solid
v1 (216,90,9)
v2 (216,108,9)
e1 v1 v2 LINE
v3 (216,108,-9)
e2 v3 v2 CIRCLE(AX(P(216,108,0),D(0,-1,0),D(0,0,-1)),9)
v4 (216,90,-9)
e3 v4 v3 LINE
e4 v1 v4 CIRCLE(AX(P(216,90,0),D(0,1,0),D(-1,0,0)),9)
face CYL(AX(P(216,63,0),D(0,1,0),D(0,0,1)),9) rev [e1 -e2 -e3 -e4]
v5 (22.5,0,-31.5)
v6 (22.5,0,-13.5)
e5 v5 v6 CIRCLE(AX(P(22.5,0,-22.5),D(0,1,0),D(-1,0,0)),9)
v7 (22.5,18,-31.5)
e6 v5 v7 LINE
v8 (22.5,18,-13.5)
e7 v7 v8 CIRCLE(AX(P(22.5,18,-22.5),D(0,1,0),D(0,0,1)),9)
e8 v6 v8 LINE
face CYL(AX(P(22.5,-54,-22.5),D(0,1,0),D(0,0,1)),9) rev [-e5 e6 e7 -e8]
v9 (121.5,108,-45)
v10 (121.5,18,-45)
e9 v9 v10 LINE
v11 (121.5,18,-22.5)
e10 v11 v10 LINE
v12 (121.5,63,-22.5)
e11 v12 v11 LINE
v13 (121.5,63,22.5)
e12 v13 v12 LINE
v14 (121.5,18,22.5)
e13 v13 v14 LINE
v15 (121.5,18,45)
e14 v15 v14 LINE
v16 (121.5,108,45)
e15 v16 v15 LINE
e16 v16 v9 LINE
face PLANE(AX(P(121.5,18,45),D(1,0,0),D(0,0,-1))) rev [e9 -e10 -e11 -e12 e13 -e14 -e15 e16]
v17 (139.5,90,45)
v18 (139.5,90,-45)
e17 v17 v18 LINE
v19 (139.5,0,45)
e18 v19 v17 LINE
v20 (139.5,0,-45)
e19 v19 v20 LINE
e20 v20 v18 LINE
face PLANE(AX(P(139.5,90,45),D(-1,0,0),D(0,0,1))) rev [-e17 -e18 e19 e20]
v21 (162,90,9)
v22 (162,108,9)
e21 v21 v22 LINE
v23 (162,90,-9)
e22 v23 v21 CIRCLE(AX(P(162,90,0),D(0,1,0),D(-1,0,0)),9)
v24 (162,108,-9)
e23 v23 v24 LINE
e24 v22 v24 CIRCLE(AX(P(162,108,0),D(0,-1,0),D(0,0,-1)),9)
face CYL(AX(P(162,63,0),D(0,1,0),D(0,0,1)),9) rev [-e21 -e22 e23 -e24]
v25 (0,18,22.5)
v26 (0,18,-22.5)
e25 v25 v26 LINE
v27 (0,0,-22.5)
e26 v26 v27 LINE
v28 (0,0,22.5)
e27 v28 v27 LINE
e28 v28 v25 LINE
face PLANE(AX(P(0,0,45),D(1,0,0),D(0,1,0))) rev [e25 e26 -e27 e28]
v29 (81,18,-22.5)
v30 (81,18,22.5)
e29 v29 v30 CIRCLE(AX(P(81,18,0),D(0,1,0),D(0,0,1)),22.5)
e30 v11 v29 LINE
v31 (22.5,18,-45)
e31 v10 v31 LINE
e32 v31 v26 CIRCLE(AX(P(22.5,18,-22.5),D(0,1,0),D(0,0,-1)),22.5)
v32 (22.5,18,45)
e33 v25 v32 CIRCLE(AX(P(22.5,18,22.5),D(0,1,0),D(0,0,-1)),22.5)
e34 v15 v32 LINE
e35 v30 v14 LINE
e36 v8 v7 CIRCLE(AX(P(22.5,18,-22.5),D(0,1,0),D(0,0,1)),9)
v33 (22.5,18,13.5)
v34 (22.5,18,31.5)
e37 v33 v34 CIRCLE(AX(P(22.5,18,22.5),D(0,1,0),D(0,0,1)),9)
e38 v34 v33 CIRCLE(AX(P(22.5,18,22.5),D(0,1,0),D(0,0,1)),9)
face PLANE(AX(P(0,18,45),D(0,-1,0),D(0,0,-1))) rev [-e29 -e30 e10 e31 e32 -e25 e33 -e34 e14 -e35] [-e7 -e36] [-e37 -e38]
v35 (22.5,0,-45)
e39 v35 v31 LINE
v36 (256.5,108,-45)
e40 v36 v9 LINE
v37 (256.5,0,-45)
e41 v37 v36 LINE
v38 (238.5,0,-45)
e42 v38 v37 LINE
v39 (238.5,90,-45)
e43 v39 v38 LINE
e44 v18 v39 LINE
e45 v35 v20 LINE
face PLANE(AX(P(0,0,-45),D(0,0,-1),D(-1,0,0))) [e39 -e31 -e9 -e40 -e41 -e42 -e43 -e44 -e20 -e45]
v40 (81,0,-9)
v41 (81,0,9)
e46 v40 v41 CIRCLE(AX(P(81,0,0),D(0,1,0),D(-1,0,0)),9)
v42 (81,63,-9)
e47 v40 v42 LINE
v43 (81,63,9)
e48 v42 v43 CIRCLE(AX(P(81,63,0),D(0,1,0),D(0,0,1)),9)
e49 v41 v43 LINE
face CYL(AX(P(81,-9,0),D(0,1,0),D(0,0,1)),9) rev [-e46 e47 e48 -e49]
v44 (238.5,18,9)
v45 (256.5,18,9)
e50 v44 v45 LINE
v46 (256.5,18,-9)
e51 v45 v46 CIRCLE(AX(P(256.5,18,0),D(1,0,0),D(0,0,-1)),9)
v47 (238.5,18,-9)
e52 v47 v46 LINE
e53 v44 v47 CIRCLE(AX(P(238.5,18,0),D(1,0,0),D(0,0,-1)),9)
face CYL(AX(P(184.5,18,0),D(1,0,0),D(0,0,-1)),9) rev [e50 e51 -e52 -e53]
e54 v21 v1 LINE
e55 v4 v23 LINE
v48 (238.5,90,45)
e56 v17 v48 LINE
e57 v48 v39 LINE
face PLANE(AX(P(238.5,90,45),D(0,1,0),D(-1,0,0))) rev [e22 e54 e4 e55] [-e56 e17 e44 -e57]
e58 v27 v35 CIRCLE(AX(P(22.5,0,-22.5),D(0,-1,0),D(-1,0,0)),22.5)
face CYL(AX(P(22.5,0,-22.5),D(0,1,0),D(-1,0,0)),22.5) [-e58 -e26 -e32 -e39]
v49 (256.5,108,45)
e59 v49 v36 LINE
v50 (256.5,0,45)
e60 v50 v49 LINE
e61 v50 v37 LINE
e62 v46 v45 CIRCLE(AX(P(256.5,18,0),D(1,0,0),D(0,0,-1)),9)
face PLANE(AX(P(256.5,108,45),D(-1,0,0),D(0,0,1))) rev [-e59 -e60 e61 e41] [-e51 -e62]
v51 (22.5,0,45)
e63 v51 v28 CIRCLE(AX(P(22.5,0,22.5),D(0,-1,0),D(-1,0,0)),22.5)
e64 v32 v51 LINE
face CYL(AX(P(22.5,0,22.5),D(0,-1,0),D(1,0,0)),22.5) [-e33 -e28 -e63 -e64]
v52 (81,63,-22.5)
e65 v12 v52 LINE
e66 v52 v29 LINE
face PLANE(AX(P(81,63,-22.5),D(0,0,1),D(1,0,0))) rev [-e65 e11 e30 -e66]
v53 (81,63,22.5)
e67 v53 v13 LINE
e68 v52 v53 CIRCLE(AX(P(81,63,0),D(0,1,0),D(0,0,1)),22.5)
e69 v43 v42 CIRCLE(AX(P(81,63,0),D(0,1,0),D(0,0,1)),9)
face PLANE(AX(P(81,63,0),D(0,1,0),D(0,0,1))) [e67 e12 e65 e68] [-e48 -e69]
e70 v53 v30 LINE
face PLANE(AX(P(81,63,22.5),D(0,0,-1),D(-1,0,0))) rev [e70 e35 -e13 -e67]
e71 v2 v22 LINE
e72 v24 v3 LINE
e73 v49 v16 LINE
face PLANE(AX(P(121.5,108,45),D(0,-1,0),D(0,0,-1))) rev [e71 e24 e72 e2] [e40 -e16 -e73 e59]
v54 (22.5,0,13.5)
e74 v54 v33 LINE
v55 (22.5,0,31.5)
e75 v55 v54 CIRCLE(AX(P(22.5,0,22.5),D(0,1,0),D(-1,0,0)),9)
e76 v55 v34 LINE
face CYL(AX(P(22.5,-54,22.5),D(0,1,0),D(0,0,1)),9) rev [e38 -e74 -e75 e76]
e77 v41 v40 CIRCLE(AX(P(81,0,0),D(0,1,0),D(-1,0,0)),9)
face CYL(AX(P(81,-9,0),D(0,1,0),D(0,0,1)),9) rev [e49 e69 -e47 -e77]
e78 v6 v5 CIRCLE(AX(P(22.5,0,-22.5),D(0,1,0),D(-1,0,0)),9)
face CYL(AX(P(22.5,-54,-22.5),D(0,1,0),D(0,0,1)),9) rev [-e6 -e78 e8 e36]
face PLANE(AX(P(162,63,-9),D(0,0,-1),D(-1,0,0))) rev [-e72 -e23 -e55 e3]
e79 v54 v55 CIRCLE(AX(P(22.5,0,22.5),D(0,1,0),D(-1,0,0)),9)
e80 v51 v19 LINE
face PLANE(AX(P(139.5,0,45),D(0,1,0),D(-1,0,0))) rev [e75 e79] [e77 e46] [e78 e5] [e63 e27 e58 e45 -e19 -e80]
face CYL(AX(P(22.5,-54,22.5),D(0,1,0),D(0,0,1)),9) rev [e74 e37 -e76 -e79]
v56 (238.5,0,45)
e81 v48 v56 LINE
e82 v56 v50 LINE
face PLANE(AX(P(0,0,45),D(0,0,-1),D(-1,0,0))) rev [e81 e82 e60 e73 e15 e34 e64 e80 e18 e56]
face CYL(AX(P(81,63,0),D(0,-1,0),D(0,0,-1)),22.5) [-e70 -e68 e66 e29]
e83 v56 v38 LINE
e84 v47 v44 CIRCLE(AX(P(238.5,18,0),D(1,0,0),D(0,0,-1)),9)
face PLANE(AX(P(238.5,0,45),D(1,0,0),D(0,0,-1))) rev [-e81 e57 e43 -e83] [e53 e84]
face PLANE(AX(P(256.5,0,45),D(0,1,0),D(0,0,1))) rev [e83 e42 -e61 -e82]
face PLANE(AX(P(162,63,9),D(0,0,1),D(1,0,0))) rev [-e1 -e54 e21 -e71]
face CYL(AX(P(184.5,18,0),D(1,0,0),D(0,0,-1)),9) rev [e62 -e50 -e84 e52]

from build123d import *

# Parameters (mm, degrees)
BRACKET_BODY_DEPTH            = 45
TOP_SLOT_18X72_DEPTH          = 45
PIVOT_BOSS_DEPTH              = 45
PIVOT_BORE_SKETCH_R           = 9
PIVOT_BORE_18_DEPTH           = 72
FLANGE_CORNER_FILLETS_R22_5_R = 22.5
FLANGE_HOLES_SKETCH_R         = 9
FLANGE_HOLES_2X_18_DEPTH      = 72
SIDE_HOLE_SKETCH_R            = 9
SIDE_HOLE_18_DEPTH            = 72


with BuildPart() as part:
    # Bracket Profile Sketch → Bracket Body (new, symmetric)
    with BuildSketch(Plane.XY):
        Polygon((0, 0), (0, 18), (121.5, 18), (121.5, 108), (256.5, 108), (256.5, 0), (238.5, 0), (238.5, 90), (139.5, 90), (139.5, 0), align=None)
    extrude(amount=BRACKET_BODY_DEPTH, both=True)

    # Top Slot Sketch → Top Slot 18x72 (cut, symmetric)
    with BuildSketch(Plane(origin=(0, 108, 0), x_dir=(1, 0, 0), z_dir=(0, 1, 0))):
        with BuildLine():
            Line((162, 9), (216, 9))
            ThreePointArc((216, 9), (225, 0), (216, -9))
            Line((216, -9), (162, -9))
            ThreePointArc((162, -9), (153, 0), (162, 9))
        make_face()
    extrude(amount=TOP_SLOT_18X72_DEPTH, both=True, mode=Mode.SUBTRACT)

    # Pivot Boss Sketch → Pivot Boss (add)
    with BuildSketch(Plane(origin=(0, 18, 0), x_dir=(1, 0, 0), z_dir=(0, 1, 0))):
        with BuildLine():
            Line((81, 22.5), (121.5, 22.5))
            Line((121.5, 22.5), (121.5, -22.5))
            Line((121.5, -22.5), (81, -22.5))
            ThreePointArc((81, -22.5), (58.5, 0), (81, 22.5))
        make_face()
    extrude(amount=PIVOT_BOSS_DEPTH)

    # Pivot Bore Sketch → Pivot Bore Ø18 (cut)
    with BuildSketch(Plane(origin=(0, 63, 0), x_dir=(1, 0, 0), z_dir=(0, 1, 0))):
        with Locations(Location((81, 0, 0), (0, 0, 270))):
            Circle(PIVOT_BORE_SKETCH_R)
    extrude(amount=-PIVOT_BORE_18_DEPTH, mode=Mode.SUBTRACT)

    # Flange Corner Fillets R22.5
    flange_corner_fillets_r22_5_edges = [part.edges().sort_by_distance(p)[0] for p in [
        (0, 9, -45),
        (0, 9, 45),
    ]]
    fillet(flange_corner_fillets_r22_5_edges, radius=FLANGE_CORNER_FILLETS_R22_5_R)

    # Flange Holes Sketch → Flange Holes 2xØ18 (cut)
    with BuildSketch(Plane(origin=(0, 18, 0), x_dir=(1, 0, 0), z_dir=(0, 1, 0))):
        with Locations(Location((22.5, 22.5, 0), (0, 0, 270))):
            Circle(FLANGE_HOLES_SKETCH_R)
        with Locations(Location((22.5, -22.5, 0), (0, 0, 270))):
            Circle(FLANGE_HOLES_SKETCH_R)
    extrude(amount=-FLANGE_HOLES_2X_18_DEPTH, mode=Mode.SUBTRACT)

    # Side Hole Sketch → Side Hole Ø18 (cut)
    with BuildSketch(Plane(origin=(256.5, 0, 0), x_dir=(0, 0, -1), z_dir=(1, 0, 0))):
        with Locations((0, 18)):
            Circle(SIDE_HOLE_SKETCH_R)
    extrude(amount=-SIDE_HOLE_18_DEPTH, mode=Mode.SUBTRACT)


solid = part.part
